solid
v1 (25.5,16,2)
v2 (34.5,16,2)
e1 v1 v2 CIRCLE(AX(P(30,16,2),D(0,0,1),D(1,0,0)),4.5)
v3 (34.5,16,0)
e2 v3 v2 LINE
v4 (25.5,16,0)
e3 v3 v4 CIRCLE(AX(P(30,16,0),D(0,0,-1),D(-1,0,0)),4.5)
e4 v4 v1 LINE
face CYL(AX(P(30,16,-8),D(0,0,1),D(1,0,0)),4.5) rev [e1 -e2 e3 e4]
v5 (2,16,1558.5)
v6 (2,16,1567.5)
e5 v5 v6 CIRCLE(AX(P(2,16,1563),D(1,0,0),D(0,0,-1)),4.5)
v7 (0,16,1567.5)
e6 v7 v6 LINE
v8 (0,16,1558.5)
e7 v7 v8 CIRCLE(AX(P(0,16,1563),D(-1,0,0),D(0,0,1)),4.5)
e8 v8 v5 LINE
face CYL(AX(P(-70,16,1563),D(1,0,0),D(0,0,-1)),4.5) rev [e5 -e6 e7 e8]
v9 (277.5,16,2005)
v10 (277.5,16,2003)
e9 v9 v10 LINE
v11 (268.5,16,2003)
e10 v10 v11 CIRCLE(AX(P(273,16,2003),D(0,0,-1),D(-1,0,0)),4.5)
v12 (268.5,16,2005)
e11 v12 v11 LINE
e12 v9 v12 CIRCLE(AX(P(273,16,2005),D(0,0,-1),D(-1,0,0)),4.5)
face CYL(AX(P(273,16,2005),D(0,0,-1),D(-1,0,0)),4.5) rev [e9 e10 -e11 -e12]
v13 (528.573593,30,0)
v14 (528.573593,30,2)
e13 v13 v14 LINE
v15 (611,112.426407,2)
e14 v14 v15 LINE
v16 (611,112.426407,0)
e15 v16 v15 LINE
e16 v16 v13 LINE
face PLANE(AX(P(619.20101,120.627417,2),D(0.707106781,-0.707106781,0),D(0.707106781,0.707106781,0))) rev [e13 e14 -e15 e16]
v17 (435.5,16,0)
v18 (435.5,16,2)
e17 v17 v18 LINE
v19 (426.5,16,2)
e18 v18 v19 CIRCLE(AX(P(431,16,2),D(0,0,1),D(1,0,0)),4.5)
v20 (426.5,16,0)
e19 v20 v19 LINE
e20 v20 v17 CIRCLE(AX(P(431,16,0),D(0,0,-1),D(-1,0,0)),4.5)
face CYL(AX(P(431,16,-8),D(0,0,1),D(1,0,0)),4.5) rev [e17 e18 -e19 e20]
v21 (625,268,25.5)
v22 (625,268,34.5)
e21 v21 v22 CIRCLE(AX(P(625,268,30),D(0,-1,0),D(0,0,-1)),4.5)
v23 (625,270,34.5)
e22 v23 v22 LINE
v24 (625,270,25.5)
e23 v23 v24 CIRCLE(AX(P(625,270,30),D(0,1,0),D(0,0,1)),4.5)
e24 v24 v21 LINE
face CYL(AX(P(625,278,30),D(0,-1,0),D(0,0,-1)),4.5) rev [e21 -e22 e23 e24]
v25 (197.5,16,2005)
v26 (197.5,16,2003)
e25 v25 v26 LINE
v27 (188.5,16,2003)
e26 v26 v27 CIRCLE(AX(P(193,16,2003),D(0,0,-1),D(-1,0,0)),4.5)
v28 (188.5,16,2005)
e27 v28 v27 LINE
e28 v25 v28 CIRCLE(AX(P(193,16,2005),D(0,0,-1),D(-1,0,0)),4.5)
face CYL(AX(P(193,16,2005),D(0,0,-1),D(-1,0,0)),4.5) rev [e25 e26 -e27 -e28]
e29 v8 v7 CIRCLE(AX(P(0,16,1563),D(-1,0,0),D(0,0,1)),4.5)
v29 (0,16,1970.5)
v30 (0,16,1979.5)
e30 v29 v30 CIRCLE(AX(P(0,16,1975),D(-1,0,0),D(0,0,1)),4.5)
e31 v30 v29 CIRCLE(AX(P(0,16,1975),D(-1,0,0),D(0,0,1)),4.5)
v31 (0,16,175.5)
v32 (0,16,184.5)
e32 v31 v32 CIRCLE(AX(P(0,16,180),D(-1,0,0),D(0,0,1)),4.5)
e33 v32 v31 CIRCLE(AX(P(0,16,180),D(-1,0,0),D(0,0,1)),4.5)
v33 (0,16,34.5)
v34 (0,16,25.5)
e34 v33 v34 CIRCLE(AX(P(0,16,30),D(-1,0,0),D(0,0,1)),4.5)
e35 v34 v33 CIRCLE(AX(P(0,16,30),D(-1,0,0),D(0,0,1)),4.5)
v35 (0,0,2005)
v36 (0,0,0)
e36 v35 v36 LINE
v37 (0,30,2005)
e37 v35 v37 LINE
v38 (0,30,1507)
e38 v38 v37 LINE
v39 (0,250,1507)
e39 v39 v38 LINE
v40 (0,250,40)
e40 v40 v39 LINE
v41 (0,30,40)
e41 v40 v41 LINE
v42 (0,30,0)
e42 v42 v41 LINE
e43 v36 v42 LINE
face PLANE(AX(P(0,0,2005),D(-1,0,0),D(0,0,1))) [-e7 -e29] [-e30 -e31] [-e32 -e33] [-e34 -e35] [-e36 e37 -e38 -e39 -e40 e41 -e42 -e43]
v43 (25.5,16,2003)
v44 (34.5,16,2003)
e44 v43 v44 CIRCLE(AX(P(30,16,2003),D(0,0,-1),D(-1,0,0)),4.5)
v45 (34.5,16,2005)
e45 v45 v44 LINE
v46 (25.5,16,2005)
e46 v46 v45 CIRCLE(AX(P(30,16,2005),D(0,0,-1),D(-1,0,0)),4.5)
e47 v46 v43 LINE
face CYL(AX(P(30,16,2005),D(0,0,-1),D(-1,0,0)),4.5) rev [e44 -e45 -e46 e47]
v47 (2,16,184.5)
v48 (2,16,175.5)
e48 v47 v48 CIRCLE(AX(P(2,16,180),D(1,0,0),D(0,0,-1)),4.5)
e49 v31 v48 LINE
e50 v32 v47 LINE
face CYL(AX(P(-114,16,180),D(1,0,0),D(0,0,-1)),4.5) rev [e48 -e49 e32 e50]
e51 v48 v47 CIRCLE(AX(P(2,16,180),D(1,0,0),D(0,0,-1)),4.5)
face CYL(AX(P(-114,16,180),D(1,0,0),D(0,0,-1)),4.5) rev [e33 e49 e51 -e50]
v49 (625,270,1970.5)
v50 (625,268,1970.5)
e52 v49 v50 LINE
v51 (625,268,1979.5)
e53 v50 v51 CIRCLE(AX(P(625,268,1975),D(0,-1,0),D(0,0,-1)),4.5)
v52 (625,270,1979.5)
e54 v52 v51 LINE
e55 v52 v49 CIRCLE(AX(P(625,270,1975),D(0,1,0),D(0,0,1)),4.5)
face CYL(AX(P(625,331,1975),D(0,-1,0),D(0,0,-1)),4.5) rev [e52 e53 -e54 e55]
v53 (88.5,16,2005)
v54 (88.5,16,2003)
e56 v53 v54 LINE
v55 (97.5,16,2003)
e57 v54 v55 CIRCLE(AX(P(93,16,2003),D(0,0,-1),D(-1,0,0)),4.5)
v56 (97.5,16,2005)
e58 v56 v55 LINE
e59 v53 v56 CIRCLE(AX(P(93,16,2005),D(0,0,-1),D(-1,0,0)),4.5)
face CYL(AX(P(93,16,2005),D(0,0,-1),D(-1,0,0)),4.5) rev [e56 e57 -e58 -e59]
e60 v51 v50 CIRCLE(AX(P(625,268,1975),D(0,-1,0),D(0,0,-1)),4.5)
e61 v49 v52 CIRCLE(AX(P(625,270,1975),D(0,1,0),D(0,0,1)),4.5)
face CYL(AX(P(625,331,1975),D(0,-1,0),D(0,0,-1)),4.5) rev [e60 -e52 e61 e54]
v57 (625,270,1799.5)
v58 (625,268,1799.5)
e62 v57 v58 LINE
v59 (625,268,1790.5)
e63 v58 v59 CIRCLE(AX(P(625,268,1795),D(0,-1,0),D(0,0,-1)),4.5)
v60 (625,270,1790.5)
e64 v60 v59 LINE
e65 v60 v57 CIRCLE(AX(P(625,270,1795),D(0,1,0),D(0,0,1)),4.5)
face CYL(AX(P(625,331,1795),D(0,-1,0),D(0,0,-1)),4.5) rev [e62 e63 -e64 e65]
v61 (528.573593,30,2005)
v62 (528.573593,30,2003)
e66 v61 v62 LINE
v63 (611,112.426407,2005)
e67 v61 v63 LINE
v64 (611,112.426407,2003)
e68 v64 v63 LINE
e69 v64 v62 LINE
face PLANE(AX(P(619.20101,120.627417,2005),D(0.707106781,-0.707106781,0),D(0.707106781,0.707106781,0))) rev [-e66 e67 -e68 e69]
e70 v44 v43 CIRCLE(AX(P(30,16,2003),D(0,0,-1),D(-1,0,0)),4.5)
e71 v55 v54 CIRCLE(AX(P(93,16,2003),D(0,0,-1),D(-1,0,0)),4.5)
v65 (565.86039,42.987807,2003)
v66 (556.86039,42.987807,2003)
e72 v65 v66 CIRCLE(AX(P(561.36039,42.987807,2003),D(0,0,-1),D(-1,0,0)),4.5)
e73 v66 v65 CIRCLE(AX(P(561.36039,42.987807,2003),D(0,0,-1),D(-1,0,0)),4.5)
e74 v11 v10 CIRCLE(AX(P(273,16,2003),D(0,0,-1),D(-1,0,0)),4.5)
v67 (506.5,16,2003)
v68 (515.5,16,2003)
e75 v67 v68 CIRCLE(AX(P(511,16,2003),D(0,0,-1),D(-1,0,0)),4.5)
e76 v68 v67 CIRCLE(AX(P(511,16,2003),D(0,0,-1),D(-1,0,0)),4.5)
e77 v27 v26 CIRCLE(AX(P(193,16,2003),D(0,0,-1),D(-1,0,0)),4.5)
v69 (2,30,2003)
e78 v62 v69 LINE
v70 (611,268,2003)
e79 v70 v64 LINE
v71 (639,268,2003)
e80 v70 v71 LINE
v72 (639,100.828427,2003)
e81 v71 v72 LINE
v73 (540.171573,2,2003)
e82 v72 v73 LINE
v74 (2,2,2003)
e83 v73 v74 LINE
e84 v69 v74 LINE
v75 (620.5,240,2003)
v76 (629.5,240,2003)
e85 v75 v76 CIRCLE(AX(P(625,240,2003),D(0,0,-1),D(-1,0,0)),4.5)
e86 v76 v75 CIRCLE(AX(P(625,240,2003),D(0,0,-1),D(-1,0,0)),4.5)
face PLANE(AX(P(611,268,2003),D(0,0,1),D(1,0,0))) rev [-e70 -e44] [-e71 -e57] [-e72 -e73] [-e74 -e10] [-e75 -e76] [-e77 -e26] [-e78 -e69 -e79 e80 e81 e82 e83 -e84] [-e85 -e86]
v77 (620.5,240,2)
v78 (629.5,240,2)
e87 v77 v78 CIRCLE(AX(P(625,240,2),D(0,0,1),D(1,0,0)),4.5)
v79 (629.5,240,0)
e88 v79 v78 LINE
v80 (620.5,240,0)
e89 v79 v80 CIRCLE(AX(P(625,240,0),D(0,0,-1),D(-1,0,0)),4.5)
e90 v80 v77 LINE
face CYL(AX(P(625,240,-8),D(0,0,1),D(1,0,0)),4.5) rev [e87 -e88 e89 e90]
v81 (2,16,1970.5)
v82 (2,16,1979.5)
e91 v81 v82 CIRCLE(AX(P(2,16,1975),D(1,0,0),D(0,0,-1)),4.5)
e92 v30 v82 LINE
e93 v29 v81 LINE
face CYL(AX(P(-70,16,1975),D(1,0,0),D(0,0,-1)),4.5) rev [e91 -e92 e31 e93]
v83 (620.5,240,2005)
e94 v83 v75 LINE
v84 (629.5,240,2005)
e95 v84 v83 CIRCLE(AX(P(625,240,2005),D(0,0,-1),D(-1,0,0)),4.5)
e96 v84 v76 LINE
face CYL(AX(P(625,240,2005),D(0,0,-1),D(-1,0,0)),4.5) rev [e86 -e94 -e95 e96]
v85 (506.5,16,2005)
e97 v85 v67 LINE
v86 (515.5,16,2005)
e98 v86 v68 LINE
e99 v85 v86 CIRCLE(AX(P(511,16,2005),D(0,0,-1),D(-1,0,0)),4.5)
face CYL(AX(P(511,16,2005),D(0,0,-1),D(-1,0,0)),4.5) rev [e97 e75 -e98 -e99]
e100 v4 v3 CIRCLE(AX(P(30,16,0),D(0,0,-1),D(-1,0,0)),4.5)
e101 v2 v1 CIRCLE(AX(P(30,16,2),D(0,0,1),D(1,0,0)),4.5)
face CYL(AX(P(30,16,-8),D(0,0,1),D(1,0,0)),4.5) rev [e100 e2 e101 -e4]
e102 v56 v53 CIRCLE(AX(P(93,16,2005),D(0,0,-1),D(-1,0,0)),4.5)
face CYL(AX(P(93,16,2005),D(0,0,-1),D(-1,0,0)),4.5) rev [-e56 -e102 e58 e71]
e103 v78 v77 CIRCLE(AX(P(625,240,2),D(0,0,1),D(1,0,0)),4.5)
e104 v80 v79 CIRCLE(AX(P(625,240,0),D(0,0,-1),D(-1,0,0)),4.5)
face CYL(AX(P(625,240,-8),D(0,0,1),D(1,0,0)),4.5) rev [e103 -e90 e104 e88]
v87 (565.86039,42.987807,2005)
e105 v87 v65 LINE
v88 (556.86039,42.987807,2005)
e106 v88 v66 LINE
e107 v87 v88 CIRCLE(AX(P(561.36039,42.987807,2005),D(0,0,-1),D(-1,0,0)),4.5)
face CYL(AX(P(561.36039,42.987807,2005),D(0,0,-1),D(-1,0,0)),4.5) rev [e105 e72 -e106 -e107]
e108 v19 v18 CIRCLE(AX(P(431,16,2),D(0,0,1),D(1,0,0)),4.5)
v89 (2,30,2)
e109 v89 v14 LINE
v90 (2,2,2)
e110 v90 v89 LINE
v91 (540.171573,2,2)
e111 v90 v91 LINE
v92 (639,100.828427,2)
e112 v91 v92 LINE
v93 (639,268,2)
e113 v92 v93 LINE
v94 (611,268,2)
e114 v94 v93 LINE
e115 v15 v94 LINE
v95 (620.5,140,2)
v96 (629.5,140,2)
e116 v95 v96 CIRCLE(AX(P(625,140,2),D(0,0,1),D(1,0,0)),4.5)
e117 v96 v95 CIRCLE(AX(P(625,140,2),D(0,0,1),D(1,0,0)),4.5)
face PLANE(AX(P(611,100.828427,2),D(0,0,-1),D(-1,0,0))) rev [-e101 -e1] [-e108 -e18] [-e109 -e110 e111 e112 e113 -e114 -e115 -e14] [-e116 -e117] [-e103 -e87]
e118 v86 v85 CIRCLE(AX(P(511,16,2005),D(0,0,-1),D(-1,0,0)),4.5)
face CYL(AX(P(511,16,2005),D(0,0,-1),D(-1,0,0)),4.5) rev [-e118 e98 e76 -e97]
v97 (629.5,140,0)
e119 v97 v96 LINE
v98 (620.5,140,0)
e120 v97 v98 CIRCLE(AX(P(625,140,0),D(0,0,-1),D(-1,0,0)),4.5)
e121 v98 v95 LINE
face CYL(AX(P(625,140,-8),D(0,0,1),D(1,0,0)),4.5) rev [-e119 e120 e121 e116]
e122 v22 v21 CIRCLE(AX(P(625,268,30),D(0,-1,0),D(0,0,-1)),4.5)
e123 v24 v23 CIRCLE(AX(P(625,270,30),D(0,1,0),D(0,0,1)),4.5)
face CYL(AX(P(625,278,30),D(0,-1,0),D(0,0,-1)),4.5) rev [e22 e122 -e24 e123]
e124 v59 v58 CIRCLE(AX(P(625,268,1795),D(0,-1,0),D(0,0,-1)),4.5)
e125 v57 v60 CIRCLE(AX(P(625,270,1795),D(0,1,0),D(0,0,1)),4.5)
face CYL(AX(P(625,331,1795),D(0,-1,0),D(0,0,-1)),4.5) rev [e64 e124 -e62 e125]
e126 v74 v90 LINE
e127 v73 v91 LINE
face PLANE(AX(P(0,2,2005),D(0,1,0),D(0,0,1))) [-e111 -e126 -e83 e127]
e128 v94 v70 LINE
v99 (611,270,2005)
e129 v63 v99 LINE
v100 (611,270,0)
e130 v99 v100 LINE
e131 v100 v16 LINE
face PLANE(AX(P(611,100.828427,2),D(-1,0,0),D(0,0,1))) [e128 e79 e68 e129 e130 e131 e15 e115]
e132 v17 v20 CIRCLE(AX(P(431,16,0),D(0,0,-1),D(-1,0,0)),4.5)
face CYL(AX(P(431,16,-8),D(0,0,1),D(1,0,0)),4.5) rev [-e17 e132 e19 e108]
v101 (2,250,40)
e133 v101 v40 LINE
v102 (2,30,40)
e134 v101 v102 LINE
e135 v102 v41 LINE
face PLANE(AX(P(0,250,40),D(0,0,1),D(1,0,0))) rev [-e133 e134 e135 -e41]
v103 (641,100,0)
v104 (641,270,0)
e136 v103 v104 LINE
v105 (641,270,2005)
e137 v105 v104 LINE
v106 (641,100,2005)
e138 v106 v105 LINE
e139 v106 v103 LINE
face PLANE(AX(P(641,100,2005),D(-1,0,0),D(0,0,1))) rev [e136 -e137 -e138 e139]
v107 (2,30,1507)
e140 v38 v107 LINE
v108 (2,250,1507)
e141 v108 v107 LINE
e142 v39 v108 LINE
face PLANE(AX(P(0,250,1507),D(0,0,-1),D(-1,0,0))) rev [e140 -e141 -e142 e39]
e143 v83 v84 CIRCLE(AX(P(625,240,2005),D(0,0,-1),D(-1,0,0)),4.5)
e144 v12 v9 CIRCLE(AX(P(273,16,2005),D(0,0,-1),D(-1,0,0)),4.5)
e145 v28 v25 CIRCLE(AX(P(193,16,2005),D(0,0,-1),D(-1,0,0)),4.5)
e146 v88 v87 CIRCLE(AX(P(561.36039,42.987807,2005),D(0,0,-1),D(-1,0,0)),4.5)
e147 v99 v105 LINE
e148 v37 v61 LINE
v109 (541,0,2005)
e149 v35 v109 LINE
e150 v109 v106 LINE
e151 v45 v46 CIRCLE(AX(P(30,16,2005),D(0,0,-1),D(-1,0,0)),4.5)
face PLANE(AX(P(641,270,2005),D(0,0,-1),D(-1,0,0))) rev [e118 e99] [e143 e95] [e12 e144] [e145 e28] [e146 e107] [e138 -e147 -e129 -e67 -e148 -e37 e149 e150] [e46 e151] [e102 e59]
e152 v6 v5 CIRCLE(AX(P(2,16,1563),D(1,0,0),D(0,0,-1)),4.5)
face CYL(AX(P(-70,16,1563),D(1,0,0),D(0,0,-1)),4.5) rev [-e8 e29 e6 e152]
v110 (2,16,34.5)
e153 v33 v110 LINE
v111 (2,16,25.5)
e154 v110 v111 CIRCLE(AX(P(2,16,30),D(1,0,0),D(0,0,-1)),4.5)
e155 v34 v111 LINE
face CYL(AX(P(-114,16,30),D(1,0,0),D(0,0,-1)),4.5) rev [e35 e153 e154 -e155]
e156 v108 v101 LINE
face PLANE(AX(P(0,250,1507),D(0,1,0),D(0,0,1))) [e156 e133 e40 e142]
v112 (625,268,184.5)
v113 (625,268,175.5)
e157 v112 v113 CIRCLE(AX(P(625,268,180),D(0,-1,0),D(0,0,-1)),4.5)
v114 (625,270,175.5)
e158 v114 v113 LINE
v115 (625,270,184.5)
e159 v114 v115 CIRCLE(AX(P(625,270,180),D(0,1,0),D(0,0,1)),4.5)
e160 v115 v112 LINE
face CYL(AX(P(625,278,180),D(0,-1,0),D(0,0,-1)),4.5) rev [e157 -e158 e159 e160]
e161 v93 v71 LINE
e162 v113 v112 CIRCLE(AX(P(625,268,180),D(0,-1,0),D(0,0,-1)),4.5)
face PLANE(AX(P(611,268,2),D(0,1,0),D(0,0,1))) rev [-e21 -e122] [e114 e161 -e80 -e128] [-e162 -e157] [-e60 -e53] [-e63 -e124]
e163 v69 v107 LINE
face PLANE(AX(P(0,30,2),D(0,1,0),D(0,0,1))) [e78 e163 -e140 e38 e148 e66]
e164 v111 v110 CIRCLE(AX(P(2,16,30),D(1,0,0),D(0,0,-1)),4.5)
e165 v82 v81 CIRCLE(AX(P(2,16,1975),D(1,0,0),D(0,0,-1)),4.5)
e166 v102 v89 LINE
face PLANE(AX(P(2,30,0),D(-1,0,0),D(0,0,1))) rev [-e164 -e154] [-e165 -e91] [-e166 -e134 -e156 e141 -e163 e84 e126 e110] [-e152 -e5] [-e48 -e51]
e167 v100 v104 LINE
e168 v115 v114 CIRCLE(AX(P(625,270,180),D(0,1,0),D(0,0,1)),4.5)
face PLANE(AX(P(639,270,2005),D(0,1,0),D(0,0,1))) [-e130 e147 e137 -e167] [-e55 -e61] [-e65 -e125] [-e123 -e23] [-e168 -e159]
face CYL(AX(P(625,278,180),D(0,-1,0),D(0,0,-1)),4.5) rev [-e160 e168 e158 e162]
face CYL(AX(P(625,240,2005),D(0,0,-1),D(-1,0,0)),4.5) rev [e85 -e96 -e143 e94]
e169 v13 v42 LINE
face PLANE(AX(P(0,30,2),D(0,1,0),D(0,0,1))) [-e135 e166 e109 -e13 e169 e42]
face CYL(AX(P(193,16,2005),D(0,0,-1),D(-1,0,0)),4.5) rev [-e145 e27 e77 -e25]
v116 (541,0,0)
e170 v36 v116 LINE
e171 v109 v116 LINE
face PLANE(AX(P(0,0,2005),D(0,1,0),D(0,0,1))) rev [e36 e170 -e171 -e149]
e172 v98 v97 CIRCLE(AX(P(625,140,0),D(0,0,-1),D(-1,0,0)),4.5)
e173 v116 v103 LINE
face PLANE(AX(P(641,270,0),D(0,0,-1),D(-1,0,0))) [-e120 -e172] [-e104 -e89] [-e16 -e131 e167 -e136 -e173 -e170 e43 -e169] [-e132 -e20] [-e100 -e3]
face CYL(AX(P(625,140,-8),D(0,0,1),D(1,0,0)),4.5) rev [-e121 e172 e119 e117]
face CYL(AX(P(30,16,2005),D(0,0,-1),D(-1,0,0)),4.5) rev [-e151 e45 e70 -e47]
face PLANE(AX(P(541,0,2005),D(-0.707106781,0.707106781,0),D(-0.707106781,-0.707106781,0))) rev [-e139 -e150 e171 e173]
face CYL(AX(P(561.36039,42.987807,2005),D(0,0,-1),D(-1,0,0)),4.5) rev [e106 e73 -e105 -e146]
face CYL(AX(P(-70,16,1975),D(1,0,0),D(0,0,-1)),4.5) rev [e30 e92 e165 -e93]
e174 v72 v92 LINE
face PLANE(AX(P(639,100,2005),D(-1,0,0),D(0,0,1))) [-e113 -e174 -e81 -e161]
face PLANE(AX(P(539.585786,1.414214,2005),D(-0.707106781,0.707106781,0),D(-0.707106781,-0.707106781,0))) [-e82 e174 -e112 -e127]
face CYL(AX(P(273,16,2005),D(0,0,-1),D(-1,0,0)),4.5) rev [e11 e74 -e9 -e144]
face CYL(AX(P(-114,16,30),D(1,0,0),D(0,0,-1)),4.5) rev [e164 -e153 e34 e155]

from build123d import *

# Parameters (mm, degrees)
EXTRUDE_1_DEPTH     = 2005
EXTRUDE_1_2_DEPTH   = 28
SKETCH_5_W          = 2
SKETCH_5_H          = 139.764501987
EXTRUDE_2_DEPTH     = 28
SKETCH_6_W          = 540.171572875
SKETCH_6_H          = 2
EXTRUDE_3_DEPTH     = 28
SKETCH_7_W          = 2
SKETCH_7_H          = 2005
EXTRUDE_4_DEPTH     = 28
SKETCH_8_W          = 2
SKETCH_8_H          = 1467
EXTRUDE_5_DEPTH     = 220
SKETCH_9_R          = 4.5
CUT_EXTRUDE_1_DEPTH = 10
SKETCH_11_R         = 4.5
CUT_EXTRUDE_2_DEPTH = 10
SKETCH_12_R         = 4.5
CUT_EXTRUDE_3_DEPTH = 116
SKETCH_13_R         = 4.5
CUT_EXTRUDE_4_DEPTH = 63
SKETCH_14_R         = 4.5
CUT_EXTRUDE_5_DEPTH = 72
CUT_EXTRUDE_START   = -2
SKETCH_15_R         = 4.5
CUT_EXTRUDE_6_DEPTH = 2


with BuildPart() as part:
    # 草图1 → Extrude 1 (new body)
    with BuildSketch(Plane.XY):
        Polygon((0, 0), (541, 0), (641, 100), (641, 270), (639, 270), (639, 100.828427125), (540.171572875, 2), (0, 2), align=None)
    extrude(amount=EXTRUDE_1_DEPTH)

    # 草图4 → Extrude 1 2 (add)
    with BuildSketch(Plane.ZY.offset(-639)):
        Polygon((0, 100.828427125), (0, 270), (2005, 270), (2005, 100.828427125), (2003, 100.828427125), (2003, 268), (2, 268), (2, 100.828427125), align=None)
    extrude(amount=EXTRUDE_1_2_DEPTH)

    # 草图5 → 凸台-拉伸2 (add)
    with BuildSketch(Plane(origin=(269.085786438, -269.085786438, 0), x_dir=(0, 0, 1), z_dir=(-0.7071067811865476, 0.7071067811865476, 0))):
        with Locations((1, 453.255446741)):
            Rectangle(SKETCH_5_W, SKETCH_5_H)
        with Locations((2004, 453.255446741)):
            Rectangle(SKETCH_5_W, SKETCH_5_H)
    extrude(amount=EXTRUDE_2_DEPTH)

    # 草图6 → 凸台-拉伸3 (add)
    with BuildSketch(Plane(origin=(0, 2, 0), x_dir=(1, 0, 0), z_dir=(0, 1, 0))):
        with Locations((270.085786438, -1)):
            Rectangle(SKETCH_6_W, SKETCH_6_H)
        with Locations((270.085786438, -2004)):
            Rectangle(SKETCH_6_W, SKETCH_6_H)
    extrude(amount=EXTRUDE_3_DEPTH)

    # 草图7 → 凸台-拉伸4 (add)
    with BuildSketch(Plane(origin=(0, 2, 0), x_dir=(1, 0, 0), z_dir=(0, 1, 0))):
        with Locations((1, -1002.5)):
            Rectangle(SKETCH_7_W, SKETCH_7_H)
    extrude(amount=EXTRUDE_4_DEPTH)

    # 草图8 → 凸台-拉伸5 (add)
    with BuildSketch(Plane(origin=(0, 30, 0), x_dir=(1, 0, 0), z_dir=(0, 1, 0))):
        with Locations((1, -773.5)):
            Rectangle(SKETCH_8_W, SKETCH_8_H)
    extrude(amount=EXTRUDE_5_DEPTH)

    # 草图9 → 切除-拉伸1 (cut)
    with BuildSketch(Plane.XY.offset(2)):
        with Locations((625, 240)):
            Circle(SKETCH_9_R)
        with Locations((30, 16)):
            Circle(SKETCH_9_R)
        with Locations((431, 16)):
            Circle(SKETCH_9_R)
        with Locations((625, 140)):
            Circle(SKETCH_9_R)
    extrude(amount=-CUT_EXTRUDE_1_DEPTH, mode=Mode.SUBTRACT)

    # 草图11 → 切除-拉伸2 (cut)
    with BuildSketch(Plane.XZ.offset(-268)):
        with Locations(Location((625, 30, 0), (0, 0, 270))):
            Circle(SKETCH_11_R)
        with Locations(Location((625, 180, 0), (0, 0, 270))):
            Circle(SKETCH_11_R)
    extrude(amount=-CUT_EXTRUDE_2_DEPTH, mode=Mode.SUBTRACT)

    # 草图12 → 切除-拉伸3 (cut)
    with BuildSketch(Plane(origin=(2, 0, 0), x_dir=(0, 0, -1), z_dir=(1, 0, 0))):
        with Locations((-30, 16)):
            Circle(SKETCH_12_R)
        with Locations((-180, 16)):
            Circle(SKETCH_12_R)
    extrude(amount=-CUT_EXTRUDE_3_DEPTH, mode=Mode.SUBTRACT)

    # 草图13 → 切除-拉伸4 (cut)
    with BuildSketch(Plane.XZ.offset(-268)):
        with Locations(Location((625, 1975, 0), (0, 0, 270))):
            Circle(SKETCH_13_R)
        with Locations(Location((625, 1795, 0), (0, 0, 270))):
            Circle(SKETCH_13_R)
    extrude(amount=-CUT_EXTRUDE_4_DEPTH, mode=Mode.SUBTRACT)

    # 草图14 → 切除-拉伸5 (cut)
    with BuildSketch(Plane(origin=(2, 0, 0), x_dir=(0, 0, -1), z_dir=(1, 0, 0))):
        with Locations((-1975, 16)):
            Circle(SKETCH_14_R)
        with Locations((-1563, 16)):
            Circle(SKETCH_14_R)
    extrude(amount=-CUT_EXTRUDE_5_DEPTH, mode=Mode.SUBTRACT)

    # 草图15 → 切除-拉伸6 (cut)
    with BuildSketch(Plane(origin=(0, 0, 2003), x_dir=(-1, 0, 0), z_dir=(0, 0, -1)).offset(CUT_EXTRUDE_START)):
        with Locations(Location((-625, 240, 0), (0, 0, 180))):
            Circle(SKETCH_15_R)
        with Locations((-561.360389693, 42.987806691)):
            Circle(SKETCH_15_R)
        with Locations(Location((-30, 16, 0), (0, 0, 180))):
            Circle(SKETCH_15_R)
        with Locations((-511, 16)):
            Circle(SKETCH_15_R)
        with Locations((-273, 16)):
            Circle(SKETCH_15_R)
        with Locations((-193, 16)):
            Circle(SKETCH_15_R)
        with Locations((-93, 16)):
            Circle(SKETCH_15_R)
    extrude(amount=CUT_EXTRUDE_6_DEPTH, mode=Mode.SUBTRACT)


solid = part.part
